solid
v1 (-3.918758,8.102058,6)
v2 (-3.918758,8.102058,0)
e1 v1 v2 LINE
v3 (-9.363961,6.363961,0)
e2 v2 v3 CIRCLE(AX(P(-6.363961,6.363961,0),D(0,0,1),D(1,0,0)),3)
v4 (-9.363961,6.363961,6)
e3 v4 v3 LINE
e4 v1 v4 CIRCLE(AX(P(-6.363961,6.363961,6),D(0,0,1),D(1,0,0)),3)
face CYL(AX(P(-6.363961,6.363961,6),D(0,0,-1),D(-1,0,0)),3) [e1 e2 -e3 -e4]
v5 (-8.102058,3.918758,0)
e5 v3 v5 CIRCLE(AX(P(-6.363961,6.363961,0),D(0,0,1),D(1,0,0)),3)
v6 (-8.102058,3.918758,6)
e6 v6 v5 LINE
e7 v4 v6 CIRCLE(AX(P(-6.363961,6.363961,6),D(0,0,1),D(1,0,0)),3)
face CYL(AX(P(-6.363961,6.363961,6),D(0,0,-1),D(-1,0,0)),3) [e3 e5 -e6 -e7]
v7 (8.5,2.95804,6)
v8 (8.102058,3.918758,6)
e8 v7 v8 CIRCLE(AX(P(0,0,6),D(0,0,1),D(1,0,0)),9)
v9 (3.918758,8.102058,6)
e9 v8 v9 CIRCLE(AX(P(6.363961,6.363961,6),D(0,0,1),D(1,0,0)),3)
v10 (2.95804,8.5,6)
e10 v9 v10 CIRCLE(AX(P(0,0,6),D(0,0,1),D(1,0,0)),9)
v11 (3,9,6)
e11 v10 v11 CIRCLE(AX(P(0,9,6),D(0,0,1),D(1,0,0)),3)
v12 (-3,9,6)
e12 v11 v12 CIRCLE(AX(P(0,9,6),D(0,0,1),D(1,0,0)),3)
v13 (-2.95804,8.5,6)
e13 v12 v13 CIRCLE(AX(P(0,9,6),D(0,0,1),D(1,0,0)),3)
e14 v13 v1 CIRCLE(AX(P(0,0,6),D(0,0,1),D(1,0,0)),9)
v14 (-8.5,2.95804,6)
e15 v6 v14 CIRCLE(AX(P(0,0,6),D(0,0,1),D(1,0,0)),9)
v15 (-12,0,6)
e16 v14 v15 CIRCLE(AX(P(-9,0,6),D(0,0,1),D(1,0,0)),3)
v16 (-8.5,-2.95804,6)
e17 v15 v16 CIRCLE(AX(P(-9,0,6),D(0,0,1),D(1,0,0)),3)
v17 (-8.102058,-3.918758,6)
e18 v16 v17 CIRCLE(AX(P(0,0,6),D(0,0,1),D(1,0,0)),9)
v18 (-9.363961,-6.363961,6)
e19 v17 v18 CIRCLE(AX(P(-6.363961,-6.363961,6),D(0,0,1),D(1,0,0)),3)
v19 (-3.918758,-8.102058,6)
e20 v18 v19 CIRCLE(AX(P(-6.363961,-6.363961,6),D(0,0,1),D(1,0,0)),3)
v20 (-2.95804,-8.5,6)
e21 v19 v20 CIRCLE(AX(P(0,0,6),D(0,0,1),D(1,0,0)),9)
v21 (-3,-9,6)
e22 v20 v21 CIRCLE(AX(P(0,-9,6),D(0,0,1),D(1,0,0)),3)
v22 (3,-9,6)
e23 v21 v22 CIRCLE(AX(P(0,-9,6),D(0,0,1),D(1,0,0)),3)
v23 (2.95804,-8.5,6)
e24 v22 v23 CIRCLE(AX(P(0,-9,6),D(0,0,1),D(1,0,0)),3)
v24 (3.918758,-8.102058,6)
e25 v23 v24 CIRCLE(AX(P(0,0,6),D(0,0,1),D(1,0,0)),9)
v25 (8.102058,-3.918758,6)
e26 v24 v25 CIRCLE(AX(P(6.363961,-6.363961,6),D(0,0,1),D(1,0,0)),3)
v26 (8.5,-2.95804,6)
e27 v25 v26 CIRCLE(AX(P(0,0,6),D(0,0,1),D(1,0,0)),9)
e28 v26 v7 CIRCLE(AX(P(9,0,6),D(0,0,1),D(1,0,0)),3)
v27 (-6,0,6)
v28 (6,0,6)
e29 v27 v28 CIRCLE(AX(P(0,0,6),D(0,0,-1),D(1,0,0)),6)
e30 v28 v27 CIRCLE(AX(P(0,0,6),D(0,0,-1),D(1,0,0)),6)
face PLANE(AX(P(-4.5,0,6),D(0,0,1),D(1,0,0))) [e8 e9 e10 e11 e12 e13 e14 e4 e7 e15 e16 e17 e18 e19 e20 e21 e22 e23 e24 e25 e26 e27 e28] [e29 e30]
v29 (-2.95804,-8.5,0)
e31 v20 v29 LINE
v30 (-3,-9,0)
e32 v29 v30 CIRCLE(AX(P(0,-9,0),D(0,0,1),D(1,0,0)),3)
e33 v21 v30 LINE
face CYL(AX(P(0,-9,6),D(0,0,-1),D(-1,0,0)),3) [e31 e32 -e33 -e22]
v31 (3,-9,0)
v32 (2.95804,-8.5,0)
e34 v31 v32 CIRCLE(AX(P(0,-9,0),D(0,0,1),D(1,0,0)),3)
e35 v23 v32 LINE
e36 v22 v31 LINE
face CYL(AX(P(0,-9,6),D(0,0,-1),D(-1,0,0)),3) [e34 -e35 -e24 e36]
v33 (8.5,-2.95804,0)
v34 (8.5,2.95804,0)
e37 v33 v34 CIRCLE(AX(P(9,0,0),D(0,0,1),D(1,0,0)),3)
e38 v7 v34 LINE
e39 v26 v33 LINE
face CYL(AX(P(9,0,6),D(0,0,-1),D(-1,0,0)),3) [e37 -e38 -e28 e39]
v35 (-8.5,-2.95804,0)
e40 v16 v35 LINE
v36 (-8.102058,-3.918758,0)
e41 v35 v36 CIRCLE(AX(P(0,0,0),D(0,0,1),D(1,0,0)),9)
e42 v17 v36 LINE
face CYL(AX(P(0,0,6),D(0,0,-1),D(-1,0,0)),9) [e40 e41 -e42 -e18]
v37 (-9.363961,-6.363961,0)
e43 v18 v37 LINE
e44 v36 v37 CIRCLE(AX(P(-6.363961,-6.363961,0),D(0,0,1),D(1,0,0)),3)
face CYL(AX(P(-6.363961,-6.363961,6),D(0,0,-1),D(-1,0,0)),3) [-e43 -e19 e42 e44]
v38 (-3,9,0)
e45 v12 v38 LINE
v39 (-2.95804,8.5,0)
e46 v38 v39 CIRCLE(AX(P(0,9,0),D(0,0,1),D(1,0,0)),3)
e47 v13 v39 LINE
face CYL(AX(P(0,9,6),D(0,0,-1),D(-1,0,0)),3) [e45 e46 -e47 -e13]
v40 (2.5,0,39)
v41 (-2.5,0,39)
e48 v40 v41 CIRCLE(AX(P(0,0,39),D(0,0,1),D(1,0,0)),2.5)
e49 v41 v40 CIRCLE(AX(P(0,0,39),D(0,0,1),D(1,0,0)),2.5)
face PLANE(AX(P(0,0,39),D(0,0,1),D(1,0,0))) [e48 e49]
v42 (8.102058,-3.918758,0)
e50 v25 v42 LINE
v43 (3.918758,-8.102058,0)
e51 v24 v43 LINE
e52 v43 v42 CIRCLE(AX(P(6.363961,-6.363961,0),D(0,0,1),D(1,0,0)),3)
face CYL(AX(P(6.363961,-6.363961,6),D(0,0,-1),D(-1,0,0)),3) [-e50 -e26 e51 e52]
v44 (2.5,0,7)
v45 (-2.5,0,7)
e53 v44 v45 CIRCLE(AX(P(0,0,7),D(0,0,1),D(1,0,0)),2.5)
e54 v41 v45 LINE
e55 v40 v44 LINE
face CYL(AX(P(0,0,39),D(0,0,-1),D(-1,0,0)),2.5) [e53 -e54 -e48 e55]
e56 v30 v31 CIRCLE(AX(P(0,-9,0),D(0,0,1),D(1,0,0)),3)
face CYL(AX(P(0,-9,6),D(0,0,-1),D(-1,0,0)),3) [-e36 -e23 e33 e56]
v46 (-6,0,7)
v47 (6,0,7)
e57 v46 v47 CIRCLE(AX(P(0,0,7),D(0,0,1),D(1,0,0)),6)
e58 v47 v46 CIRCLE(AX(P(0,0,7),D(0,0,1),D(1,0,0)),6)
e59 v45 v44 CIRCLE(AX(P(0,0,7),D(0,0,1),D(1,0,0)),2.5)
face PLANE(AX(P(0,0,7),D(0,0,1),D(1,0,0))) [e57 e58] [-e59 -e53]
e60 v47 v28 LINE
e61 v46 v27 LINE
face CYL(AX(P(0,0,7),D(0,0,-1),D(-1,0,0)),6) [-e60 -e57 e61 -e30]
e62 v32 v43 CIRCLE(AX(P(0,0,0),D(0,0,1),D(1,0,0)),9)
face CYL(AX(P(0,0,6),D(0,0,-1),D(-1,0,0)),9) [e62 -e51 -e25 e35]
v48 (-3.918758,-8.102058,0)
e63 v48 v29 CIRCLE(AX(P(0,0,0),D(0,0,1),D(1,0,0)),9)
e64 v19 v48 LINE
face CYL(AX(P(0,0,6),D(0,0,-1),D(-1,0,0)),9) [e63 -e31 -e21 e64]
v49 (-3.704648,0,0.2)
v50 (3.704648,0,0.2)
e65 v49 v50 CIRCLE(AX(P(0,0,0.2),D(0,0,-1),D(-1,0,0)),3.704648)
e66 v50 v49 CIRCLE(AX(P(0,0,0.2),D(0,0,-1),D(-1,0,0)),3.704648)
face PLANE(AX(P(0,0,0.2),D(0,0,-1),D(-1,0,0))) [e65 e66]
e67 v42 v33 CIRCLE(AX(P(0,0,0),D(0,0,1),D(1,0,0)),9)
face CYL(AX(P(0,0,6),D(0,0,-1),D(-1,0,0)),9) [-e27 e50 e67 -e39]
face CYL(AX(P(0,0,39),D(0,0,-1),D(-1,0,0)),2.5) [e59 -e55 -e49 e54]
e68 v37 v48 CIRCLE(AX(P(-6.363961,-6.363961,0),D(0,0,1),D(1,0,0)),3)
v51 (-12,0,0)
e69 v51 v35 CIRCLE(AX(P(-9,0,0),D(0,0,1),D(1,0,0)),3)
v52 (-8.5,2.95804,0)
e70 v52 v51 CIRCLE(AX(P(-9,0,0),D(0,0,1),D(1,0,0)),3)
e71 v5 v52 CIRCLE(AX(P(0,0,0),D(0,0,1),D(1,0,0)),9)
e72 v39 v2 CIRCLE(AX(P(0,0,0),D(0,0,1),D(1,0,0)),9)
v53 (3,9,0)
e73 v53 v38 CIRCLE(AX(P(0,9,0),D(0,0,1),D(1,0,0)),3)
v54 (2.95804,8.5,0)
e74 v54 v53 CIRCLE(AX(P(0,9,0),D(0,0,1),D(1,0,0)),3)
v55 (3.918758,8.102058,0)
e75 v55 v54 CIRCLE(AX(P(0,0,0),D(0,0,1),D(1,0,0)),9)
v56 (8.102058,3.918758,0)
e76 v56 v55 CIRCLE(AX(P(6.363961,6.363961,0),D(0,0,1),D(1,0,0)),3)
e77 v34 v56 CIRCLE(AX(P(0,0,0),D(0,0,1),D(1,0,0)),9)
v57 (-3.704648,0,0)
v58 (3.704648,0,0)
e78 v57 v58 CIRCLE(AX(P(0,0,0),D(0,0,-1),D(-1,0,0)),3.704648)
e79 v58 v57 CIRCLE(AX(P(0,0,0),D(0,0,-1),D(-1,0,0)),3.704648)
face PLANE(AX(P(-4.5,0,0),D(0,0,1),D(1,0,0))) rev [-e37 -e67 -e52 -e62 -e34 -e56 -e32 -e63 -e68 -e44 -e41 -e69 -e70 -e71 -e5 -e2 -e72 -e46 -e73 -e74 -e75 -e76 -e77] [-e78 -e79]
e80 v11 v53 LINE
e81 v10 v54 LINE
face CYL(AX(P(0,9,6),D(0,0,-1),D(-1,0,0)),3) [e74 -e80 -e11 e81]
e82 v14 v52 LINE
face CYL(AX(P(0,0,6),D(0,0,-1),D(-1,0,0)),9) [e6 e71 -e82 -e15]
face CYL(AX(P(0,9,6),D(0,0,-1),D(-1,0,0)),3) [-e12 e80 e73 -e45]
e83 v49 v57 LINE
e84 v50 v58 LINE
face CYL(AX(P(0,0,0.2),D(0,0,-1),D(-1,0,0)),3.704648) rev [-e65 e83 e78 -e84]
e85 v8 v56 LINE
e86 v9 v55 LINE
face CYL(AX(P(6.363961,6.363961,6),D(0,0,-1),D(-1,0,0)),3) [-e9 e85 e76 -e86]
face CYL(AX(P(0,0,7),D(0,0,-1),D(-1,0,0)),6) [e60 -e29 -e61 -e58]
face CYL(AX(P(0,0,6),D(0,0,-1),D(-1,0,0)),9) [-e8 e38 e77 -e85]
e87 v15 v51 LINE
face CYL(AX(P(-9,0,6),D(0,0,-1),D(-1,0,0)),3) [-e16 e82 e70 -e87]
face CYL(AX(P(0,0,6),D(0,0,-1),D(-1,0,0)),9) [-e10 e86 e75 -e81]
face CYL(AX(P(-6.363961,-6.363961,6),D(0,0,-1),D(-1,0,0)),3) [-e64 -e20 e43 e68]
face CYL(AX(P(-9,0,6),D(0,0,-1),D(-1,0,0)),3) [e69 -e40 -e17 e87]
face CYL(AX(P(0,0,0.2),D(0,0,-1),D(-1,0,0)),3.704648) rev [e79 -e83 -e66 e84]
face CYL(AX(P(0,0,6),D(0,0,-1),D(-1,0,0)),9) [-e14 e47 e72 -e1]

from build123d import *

# Parameters (mm, degrees)
BOSS_EXTRUDE1_DEPTH = 6
SKETCH2_R           = 2.5
BOSS_EXTRUDE2_DEPTH = 33
SKETCH3_R           = 6
BOSS_EXTRUDE3_DEPTH = 1
SKETCH4_R           = 3.704648002
CUT_EXTRUDE1_DEPTH  = 0.2


with BuildPart() as part:
    # Sketch1 → Boss-Extrude1 (new body)
    with BuildSketch(Plane.XY):
        with BuildLine():
            ThreePointArc((-8.5, -2.958039892), (-8.314915793, -3.444150891), (-8.102057706, -3.918757574))
            ThreePointArc((-8.102057706, -3.918757574), (-8.485281374, -8.485281374), (-3.918757574, -8.102057706))
            ThreePointArc((-3.918757574, -8.102057706), (-3.444150891, -8.314915793), (-2.958039892, -8.5))
            ThreePointArc((-2.958039892, -8.5), (0, -12), (2.958039892, -8.5))
            ThreePointArc((2.958039892, -8.5), (3.444150891, -8.314915793), (3.918757574, -8.102057706))
            ThreePointArc((3.918757574, -8.102057706), (8.485281374, -8.485281374), (8.102057706, -3.918757574))
            ThreePointArc((8.102057706, -3.918757574), (8.314915793, -3.444150891), (8.5, -2.958039892))
            ThreePointArc((8.5, -2.958039892), (12, 0), (8.5, 2.958039892))
            ThreePointArc((8.5, 2.958039892), (8.314915793, 3.444150891), (8.102057706, 3.918757574))
            ThreePointArc((8.102057706, 3.918757574), (8.485281374, 8.485281374), (3.918757574, 8.102057706))
            ThreePointArc((3.918757574, 8.102057706), (3.444150891, 8.314915793), (2.958039892, 8.5))
            ThreePointArc((2.958039892, 8.5), (0, 12), (-2.958039892, 8.5))
            ThreePointArc((-2.958039892, 8.5), (-3.444150891, 8.314915793), (-3.918757574, 8.102057706))
            ThreePointArc((-3.918757574, 8.102057706), (-8.485281374, 8.485281374), (-8.102057706, 3.918757574))
            ThreePointArc((-8.102057706, 3.918757574), (-8.314915793, 3.444150891), (-8.5, 2.958039892))
            ThreePointArc((-8.5, 2.958039892), (-12, 0), (-8.5, -2.958039892))
        make_face()
    extrude(amount=BOSS_EXTRUDE1_DEPTH)

    # Sketch2 → Boss-Extrude2 (add)
    with BuildSketch(Plane.XY.offset(6)):
        Circle(SKETCH2_R)
    extrude(amount=BOSS_EXTRUDE2_DEPTH)

    # Sketch3 → Boss-Extrude3 (add, symmetric)
    with BuildSketch(Plane.XY.offset(6)):
        Circle(SKETCH3_R)
    extrude(amount=BOSS_EXTRUDE3_DEPTH, both=True)

    # Sketch4 → Cut-Extrude1 (cut)
    with BuildSketch(Plane(origin=(0, 0, 0), x_dir=(-1, 0, 0), z_dir=(0, 0, -1))):
        Circle(SKETCH4_R)
    extrude(amount=-CUT_EXTRUDE1_DEPTH, mode=Mode.SUBTRACT)


solid = part.part
